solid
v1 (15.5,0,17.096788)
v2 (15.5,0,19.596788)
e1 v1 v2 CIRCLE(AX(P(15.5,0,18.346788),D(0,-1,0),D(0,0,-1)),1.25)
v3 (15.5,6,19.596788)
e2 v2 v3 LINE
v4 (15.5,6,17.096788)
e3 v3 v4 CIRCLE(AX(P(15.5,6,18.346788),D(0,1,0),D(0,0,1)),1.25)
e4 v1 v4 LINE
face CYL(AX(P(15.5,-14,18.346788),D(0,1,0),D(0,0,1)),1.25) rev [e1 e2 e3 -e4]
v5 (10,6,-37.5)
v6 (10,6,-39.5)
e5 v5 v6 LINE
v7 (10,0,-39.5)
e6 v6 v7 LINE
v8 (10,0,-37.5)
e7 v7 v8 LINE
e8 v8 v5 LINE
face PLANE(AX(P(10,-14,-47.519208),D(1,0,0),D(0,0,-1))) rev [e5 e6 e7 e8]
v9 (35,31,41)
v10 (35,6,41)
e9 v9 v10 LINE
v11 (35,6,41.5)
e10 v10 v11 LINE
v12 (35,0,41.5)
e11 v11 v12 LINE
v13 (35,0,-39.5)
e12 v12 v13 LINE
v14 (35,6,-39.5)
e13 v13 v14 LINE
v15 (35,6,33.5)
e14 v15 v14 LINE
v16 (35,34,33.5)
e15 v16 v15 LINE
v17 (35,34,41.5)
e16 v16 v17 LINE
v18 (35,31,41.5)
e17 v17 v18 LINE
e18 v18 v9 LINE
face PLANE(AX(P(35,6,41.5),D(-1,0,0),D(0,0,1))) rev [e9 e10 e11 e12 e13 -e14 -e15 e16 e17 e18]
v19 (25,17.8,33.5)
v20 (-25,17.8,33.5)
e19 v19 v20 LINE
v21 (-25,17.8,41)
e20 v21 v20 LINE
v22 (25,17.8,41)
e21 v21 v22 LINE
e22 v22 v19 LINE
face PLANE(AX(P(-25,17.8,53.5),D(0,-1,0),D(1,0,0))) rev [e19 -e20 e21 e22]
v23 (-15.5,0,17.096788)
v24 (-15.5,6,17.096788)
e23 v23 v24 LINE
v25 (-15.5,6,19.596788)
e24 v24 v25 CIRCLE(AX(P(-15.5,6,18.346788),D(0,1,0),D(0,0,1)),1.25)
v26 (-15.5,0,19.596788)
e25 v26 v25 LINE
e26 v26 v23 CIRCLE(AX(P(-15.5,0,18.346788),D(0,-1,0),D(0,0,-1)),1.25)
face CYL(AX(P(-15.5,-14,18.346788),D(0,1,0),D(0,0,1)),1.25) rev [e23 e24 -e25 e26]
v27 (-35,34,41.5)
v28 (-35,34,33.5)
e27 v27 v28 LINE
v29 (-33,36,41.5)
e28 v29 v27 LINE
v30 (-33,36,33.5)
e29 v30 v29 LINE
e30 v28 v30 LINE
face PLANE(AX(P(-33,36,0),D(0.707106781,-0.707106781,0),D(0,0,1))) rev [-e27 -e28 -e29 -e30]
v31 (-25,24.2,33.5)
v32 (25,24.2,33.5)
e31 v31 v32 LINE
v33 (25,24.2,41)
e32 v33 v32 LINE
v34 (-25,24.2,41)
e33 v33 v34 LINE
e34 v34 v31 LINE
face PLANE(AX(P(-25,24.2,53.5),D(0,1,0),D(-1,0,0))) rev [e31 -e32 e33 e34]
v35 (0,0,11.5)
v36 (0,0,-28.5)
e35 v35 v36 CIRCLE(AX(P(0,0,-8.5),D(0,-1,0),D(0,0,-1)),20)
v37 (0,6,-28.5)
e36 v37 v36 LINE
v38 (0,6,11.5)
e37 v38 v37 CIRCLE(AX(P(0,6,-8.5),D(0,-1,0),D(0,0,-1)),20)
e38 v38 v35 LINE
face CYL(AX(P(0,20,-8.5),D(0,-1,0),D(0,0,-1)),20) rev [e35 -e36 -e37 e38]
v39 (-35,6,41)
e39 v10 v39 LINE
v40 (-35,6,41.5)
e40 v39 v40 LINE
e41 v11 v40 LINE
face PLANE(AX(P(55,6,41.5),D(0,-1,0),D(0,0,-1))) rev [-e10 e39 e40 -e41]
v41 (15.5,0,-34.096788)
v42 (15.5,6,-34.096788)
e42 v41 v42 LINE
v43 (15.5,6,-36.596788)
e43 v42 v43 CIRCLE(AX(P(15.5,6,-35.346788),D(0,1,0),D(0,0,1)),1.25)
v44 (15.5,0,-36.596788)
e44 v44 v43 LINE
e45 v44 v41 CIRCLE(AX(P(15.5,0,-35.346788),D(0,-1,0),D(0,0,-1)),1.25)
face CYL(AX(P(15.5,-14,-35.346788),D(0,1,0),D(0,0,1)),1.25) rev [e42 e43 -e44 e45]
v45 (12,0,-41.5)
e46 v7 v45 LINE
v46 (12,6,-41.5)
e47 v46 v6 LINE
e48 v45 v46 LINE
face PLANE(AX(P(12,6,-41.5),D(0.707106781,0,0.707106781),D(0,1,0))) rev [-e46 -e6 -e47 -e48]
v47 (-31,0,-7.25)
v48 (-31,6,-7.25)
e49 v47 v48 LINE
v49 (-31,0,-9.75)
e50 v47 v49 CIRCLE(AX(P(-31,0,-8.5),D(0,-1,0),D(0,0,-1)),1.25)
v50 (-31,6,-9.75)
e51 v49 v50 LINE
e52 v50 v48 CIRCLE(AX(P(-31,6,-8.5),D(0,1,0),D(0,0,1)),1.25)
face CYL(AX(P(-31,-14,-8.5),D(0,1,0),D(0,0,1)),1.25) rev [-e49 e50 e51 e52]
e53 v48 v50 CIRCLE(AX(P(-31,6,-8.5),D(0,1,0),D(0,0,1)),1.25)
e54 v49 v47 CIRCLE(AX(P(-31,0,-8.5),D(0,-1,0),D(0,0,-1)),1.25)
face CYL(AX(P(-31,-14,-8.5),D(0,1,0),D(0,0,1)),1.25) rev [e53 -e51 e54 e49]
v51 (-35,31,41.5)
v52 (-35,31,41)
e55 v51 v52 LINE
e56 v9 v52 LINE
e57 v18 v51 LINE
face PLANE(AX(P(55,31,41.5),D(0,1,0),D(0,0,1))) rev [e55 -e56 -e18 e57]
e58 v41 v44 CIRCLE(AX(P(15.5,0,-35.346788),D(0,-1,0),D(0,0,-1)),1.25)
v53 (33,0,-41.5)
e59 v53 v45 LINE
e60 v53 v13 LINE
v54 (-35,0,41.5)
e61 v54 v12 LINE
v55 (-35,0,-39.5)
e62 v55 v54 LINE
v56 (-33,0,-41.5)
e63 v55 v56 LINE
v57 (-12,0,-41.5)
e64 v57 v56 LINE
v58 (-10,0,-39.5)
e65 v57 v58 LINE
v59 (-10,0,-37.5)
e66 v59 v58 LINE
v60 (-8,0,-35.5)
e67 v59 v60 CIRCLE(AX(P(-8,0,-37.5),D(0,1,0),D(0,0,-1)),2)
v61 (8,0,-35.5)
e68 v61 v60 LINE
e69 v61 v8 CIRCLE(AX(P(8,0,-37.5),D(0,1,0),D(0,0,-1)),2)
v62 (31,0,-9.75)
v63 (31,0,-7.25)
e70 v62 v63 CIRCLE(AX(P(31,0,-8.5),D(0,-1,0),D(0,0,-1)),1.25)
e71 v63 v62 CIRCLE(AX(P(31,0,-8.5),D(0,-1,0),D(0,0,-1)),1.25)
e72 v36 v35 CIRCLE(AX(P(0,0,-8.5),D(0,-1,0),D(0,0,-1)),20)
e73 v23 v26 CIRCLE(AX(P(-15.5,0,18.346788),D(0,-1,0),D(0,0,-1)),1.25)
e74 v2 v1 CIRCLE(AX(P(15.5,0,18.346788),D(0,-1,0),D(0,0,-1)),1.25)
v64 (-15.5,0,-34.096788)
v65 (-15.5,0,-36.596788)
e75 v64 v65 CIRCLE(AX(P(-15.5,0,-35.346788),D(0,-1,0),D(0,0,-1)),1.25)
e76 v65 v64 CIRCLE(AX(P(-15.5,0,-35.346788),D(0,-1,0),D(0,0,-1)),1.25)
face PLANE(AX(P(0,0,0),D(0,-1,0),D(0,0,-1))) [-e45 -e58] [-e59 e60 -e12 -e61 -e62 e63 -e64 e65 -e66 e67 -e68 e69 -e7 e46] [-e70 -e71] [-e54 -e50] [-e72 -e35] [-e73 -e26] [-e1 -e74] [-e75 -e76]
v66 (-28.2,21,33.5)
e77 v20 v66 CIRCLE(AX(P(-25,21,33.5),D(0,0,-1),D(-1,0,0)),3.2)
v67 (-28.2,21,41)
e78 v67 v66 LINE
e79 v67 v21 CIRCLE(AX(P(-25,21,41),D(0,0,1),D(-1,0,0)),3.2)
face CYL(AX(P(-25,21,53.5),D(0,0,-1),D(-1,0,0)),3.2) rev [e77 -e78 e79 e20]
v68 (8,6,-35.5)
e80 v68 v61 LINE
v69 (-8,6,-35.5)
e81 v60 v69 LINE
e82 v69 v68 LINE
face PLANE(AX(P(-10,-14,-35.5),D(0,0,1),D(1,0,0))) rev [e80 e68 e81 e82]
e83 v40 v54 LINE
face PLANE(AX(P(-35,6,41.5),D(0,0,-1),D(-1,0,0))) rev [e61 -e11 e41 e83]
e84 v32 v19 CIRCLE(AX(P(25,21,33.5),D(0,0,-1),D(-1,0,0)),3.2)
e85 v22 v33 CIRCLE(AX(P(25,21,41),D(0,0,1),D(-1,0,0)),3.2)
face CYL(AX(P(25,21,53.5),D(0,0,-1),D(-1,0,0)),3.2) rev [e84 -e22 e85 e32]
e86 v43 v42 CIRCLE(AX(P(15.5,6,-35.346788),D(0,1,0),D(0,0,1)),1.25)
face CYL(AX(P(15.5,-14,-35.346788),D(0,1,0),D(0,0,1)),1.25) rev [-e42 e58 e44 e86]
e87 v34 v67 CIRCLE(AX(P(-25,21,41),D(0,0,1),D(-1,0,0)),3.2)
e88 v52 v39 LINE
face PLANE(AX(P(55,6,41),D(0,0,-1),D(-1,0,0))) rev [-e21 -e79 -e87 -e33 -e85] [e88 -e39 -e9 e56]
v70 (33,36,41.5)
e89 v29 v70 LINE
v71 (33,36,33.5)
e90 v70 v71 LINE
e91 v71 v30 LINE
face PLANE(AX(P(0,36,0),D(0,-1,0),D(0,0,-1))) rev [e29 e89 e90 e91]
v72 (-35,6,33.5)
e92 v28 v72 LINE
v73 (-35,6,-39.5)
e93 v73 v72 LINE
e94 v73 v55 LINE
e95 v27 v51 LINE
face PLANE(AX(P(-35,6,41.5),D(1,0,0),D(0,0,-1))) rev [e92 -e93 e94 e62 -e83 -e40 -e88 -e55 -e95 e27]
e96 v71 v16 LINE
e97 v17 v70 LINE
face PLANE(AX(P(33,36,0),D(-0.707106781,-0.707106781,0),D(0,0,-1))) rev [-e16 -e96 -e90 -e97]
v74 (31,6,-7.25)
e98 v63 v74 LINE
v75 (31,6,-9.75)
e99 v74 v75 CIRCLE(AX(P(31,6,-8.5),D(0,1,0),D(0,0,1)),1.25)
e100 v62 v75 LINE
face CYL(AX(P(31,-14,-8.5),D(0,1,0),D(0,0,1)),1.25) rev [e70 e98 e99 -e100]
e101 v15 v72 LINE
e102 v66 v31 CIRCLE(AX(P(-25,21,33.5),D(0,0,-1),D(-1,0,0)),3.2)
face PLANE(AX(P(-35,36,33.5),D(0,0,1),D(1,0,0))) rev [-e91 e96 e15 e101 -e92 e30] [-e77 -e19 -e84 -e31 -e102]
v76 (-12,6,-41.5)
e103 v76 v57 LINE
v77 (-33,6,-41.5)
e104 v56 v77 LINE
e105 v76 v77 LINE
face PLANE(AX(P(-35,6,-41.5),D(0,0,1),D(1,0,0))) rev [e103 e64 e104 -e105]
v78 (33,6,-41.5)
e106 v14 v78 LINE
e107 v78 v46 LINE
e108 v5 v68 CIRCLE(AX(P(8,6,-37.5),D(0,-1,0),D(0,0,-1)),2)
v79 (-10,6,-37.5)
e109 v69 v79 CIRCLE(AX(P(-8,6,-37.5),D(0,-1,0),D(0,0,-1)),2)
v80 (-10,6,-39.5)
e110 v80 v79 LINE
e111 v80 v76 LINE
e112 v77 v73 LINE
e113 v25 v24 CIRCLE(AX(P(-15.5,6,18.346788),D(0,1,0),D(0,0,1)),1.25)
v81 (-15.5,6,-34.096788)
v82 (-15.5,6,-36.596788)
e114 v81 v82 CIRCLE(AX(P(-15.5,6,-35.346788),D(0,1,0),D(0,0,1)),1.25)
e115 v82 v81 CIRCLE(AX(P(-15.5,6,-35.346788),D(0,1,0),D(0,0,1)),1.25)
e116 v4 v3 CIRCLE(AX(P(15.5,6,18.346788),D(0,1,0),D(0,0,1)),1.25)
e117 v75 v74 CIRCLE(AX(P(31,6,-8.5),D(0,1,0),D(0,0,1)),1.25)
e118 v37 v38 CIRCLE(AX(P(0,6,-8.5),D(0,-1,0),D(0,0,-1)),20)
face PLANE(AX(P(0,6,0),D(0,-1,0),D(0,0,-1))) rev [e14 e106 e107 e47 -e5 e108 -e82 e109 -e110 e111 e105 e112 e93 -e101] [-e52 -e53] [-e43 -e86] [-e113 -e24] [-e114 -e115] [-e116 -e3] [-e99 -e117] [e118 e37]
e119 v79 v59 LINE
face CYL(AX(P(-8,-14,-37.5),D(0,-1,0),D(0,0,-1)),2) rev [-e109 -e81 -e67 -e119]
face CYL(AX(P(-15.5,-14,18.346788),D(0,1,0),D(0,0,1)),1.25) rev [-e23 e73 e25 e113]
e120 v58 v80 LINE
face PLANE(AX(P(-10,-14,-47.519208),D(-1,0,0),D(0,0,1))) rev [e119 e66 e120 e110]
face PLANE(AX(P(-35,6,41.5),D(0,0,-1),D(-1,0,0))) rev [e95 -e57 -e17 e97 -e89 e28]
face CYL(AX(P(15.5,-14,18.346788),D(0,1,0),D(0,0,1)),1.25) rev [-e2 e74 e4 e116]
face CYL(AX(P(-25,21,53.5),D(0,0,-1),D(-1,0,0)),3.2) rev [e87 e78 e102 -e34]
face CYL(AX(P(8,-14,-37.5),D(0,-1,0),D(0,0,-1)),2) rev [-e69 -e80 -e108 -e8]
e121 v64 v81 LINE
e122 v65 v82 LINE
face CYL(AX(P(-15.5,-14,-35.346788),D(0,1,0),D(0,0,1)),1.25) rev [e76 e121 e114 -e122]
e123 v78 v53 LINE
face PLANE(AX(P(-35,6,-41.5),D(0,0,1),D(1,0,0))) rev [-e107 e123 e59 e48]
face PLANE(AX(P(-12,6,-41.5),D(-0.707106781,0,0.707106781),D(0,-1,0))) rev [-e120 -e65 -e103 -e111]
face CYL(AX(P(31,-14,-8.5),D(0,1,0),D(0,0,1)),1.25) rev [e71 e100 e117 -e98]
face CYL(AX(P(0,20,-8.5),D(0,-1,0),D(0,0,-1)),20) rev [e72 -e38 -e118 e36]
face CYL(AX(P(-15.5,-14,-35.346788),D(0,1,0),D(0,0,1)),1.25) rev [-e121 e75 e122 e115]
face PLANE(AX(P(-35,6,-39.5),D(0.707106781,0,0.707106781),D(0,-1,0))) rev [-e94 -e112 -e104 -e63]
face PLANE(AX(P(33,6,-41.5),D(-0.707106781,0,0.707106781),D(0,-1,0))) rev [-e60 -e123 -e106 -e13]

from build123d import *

# Parameters (mm, degrees)
SKETCH1_W           = 70
SKETCH1_H           = 83
BOSS_EXTRUDE1_DEPTH = 6
SKETCH2_W           = 70
SKETCH2_H           = 8
BOSS_EXTRUDE2_DEPTH = 30
SKETCH3_R           = 20
CUT_EXTRUDE1_DEPTH  = 20
SKETCH4_W           = 20
SKETCH4_H           = 12.019208042
CUT_EXTRUDE2_DEPTH  = 20
SKETCH5_R           = 1.25
CUT_EXTRUDE3_DEPTH  = 20
CUT_EXTRUDE4_DEPTH  = 20
SKETCH7_W           = 0.5
SKETCH7_H           = 25
CUT_EXTRUDE5_DEPTH  = 90
FILLET1_R           = 2
CHAMFER1_SIZE       = 2


with BuildPart() as part:
    # Sketch1 → Boss-Extrude1 (new body)
    with BuildSketch(Plane(origin=(0, 0, 0), x_dir=(1, 0, 0), z_dir=(0, 1, 0))):
        Rectangle(SKETCH1_W, SKETCH1_H)
    extrude(amount=BOSS_EXTRUDE1_DEPTH)

    # Sketch2 → Boss-Extrude2 (add)
    with BuildSketch(Plane(origin=(0, 6, 0), x_dir=(1, 0, 0), z_dir=(0, 1, 0))):
        with Locations((0, -37.5)):
            Rectangle(SKETCH2_W, SKETCH2_H)
    extrude(amount=BOSS_EXTRUDE2_DEPTH)

    # Sketch3 → Cut-Extrude1 (cut)
    with BuildSketch(Plane.XZ):
        with Locations(Location((0, -8.5, 0), (0, 0, 270))):
            Circle(SKETCH3_R)
    extrude(amount=-CUT_EXTRUDE1_DEPTH, mode=Mode.SUBTRACT)

    # Sketch4 → Cut-Extrude2 (cut)
    with BuildSketch(Plane(origin=(0, 6, 0), x_dir=(1, 0, 0), z_dir=(0, 1, 0))):
        with Locations((0, 41.509604021)):
            Rectangle(SKETCH4_W, SKETCH4_H)
    extrude(amount=-CUT_EXTRUDE2_DEPTH, mode=Mode.SUBTRACT)

    # Sketch5 → Cut-Extrude3 (cut)
    with BuildSketch(Plane(origin=(0, 6, 0), x_dir=(1, 0, 0), z_dir=(0, 1, 0))):
        with Locations(Location((31, 8.5, 0), (0, 0, 270))):
            Circle(SKETCH5_R)
        with Locations(Location((15.5, -18.346787517, 0), (0, 0, 270))):
            Circle(SKETCH5_R)
        with Locations(Location((-15.5, -18.346787517, 0), (0, 0, 270))):
            Circle(SKETCH5_R)
        with Locations(Location((-31, 8.5, 0), (0, 0, 270))):
            Circle(SKETCH5_R)
        with Locations(Location((-15.5, 35.346787517, 0), (0, 0, 270))):
            Circle(SKETCH5_R)
        with Locations(Location((15.5, 35.346787517, 0), (0, 0, 270))):
            Circle(SKETCH5_R)
    extrude(amount=-CUT_EXTRUDE3_DEPTH, mode=Mode.SUBTRACT)

    # Sketch6 → Cut-Extrude4 (cut)
    with BuildSketch(Plane(origin=(0, 0, 33.5), x_dir=(-1, 0, 0), z_dir=(0, 0, -1))):
        with BuildLine():
            Line((25, 17.8), (-25, 17.8))
            ThreePointArc((-25, 17.8), (-28.2, 21), (-25, 24.2))
            Line((-25, 24.2), (25, 24.2))
            ThreePointArc((25, 24.2), (28.2, 21), (25, 17.8))
        make_face()
    extrude(amount=-CUT_EXTRUDE4_DEPTH, mode=Mode.SUBTRACT)

    # Sketch7 → Cut-Extrude5 (cut)
    with BuildSketch(Plane.ZY.offset(35)):
        with Locations((41.25, 18.5)):
            Rectangle(SKETCH7_W, SKETCH7_H)
    extrude(amount=-CUT_EXTRUDE5_DEPTH, mode=Mode.SUBTRACT)

    # Fillet1
    fillet1_edges = [part.edges().sort_by_distance(p)[0] for p in [
        (-10, 3, -35.5),
        (10, 3, -35.5),
    ]]
    fillet(fillet1_edges, radius=FILLET1_R)

    # Chamfer1
    chamfer1_edges = [part.edges().sort_by_distance(p)[0] for p in [
        (-35, 36, 37.5),
        (35, 36, 37.5),
        (-10, 3, -41.5),
        (10, 3, -41.5),
        (-35, 3, -41.5),
        (35, 3, -41.5),
    ]]
    chamfer(chamfer1_edges, length=CHAMFER1_SIZE)


solid = part.part
